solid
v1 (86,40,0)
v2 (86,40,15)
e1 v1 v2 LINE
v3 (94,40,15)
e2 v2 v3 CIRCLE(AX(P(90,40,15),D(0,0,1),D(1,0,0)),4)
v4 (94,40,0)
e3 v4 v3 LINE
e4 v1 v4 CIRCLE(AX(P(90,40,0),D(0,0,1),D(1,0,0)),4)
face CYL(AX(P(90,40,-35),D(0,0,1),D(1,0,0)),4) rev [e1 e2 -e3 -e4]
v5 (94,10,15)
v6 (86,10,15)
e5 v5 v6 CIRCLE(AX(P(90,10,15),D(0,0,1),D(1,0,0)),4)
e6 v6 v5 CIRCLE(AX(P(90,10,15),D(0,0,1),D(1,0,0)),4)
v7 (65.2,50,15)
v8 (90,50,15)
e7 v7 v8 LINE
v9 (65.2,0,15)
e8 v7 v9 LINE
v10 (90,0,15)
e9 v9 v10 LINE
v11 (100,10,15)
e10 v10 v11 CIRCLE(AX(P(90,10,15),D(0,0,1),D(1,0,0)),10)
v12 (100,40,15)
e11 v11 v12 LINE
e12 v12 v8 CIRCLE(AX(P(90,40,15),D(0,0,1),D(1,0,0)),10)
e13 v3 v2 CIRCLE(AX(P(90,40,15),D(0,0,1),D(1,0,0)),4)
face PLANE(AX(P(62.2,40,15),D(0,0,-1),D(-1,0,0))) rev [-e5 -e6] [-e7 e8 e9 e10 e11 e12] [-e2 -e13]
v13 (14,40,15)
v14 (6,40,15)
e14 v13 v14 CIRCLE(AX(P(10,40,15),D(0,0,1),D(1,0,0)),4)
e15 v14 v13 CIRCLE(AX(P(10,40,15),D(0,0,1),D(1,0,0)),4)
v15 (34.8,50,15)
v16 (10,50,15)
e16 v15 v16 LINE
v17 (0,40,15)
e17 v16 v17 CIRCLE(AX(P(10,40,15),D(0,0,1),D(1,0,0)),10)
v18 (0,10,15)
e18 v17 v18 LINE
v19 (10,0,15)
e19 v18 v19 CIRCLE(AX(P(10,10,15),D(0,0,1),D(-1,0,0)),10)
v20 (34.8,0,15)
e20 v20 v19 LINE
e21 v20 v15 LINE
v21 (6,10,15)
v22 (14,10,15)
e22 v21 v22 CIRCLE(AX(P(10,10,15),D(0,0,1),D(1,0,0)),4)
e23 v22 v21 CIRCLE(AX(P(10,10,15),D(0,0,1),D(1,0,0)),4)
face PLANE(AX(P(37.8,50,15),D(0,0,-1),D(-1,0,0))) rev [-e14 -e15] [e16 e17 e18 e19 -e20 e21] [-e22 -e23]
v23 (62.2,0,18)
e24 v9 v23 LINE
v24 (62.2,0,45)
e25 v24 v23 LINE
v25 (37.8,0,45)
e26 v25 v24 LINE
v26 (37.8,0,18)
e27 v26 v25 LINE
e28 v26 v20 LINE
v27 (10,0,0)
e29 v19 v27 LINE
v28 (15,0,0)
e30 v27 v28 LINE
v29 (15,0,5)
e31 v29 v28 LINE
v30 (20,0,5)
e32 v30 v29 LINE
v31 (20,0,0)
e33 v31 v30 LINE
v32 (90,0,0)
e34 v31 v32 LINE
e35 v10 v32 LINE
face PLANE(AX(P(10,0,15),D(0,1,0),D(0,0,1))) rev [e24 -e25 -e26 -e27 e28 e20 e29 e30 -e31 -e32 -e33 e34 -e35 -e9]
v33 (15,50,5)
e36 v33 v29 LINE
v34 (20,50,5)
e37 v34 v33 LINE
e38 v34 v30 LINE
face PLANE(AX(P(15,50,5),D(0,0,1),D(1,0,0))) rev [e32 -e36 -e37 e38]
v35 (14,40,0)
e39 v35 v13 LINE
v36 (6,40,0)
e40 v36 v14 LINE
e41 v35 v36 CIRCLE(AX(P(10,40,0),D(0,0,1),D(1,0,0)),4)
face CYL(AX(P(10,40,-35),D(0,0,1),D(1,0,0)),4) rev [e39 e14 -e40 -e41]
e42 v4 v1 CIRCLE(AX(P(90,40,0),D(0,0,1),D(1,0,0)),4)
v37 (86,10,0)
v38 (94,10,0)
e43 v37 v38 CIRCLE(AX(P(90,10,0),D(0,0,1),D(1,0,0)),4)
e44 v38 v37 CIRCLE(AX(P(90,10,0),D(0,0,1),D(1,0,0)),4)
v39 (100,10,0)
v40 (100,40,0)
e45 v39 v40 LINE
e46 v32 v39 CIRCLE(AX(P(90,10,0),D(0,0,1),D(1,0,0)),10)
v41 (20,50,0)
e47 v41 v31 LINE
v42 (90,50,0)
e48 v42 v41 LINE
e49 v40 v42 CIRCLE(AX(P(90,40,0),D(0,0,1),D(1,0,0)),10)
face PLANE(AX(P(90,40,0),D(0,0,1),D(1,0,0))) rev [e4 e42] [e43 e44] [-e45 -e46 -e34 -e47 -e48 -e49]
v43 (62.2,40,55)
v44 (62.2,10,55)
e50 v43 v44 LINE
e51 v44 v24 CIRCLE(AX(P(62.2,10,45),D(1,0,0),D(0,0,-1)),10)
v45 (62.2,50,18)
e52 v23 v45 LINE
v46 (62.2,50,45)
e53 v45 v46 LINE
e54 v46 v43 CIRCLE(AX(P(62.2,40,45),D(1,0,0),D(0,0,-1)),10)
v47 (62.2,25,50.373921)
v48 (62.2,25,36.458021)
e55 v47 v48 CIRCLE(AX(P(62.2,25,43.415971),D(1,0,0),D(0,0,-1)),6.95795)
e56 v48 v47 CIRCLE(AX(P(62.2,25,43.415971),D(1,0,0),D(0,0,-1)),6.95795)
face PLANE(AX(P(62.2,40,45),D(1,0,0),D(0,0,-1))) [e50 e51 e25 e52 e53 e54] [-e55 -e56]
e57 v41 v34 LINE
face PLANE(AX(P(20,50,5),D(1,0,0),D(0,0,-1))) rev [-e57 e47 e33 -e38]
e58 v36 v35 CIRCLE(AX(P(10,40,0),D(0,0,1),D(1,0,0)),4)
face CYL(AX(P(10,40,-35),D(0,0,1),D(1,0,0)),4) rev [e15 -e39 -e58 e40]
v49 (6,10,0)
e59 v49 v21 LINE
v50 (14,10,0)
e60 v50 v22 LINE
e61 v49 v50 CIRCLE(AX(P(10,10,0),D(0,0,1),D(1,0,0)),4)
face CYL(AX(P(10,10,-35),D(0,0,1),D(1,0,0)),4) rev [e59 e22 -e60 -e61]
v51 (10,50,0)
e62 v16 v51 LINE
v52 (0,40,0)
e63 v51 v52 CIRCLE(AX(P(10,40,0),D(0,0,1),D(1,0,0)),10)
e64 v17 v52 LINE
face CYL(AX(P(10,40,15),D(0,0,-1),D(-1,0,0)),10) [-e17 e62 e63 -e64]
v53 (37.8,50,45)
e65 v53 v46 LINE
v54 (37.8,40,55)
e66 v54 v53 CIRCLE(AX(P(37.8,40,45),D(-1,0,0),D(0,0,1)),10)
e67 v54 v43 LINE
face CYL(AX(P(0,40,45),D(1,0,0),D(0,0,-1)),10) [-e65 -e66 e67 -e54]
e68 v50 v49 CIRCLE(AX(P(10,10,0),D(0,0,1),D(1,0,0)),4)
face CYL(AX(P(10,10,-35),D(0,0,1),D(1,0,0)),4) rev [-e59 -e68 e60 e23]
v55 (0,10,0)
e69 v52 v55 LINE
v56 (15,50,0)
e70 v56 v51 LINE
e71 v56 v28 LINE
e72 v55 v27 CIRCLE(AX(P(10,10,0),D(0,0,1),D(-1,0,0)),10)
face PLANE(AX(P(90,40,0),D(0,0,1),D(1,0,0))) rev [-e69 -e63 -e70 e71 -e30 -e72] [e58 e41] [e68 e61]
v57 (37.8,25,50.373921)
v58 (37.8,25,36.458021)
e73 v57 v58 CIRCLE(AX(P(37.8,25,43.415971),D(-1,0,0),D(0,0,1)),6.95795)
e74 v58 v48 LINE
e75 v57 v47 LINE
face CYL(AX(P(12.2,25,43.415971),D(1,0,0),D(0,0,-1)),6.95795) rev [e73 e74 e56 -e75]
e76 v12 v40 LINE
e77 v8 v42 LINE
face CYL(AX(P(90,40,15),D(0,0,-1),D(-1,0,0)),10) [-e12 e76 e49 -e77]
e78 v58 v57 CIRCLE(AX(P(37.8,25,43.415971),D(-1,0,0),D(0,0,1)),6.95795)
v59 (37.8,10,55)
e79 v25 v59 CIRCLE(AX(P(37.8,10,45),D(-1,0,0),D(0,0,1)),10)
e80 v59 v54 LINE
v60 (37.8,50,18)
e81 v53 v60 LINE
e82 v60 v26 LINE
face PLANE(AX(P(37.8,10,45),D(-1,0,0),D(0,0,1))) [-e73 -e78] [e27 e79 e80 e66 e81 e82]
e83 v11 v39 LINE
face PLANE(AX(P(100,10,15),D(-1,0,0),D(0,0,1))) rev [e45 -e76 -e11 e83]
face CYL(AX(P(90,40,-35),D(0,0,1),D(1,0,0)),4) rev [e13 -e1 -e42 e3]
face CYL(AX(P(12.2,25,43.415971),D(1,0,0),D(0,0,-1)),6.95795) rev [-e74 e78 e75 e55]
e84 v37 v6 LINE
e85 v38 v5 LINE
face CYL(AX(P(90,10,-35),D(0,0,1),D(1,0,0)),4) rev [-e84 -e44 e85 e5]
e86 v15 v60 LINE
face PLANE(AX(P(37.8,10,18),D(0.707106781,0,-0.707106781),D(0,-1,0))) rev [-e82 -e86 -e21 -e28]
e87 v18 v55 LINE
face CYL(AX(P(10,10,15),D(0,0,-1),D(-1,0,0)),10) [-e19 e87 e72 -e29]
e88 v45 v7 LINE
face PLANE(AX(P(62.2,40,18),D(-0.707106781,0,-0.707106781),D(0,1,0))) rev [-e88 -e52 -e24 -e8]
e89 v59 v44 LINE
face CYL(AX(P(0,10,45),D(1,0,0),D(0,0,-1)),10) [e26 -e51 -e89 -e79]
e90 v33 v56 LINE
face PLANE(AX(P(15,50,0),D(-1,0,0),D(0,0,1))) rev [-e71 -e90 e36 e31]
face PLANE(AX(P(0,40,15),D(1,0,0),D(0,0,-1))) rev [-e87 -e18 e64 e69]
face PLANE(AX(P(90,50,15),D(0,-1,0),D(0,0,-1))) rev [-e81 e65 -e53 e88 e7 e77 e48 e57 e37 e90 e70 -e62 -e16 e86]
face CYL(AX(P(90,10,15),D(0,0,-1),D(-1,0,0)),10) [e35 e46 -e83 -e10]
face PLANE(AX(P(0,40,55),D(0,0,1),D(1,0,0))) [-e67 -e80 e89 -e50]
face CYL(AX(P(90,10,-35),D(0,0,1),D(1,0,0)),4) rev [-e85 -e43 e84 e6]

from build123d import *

# Parameters (mm, degrees)
BASE_PLATE_DEPTH              = 15
KNUCKLE_BLOCK_DEPTH           = 100
KNUCKLE_RELIEF_CUT_A_DEPTH    = 37.8
KNUCKLE_START                 = -37.8
KNUCKLE_RELIEF_CUT_B_DEPTH    = 37.8
PLATE_MOUNTING_HOLES_SKETCH_W = 5
PLATE_MOUNTING_HOLES_SKETCH_H = 5
PLATE_MOUNTING_HOLES_DEPTH    = 50
HINGE_PIN_HOLE_SKETCH_R       = 6.957950298
HINGE_PIN_HOLE_DEPTH          = 50
UPPER_MOUNTING_HOLES_SKETCH_R = 4
UPPER_MOUNTING_HOLES_DEPTH    = 50
KNUCKLE_CHAMFER_A_3X45_SIZE   = 3
KNUCKLE_CHAMFER_B_3X45_SIZE   = 3


with BuildPart() as part:
    # Base Plate Sketch → Base Plate (new body)
    with BuildSketch(Plane.XY):
        with BuildLine():
            Line((10, 0), (90, 0))
            ThreePointArc((90, 0), (97.071067812, 2.928932188), (100, 10))
            Line((100, 10), (100, 40))
            ThreePointArc((100, 40), (97.071067812, 47.071067812), (90, 50))
            Line((90, 50), (10, 50))
            ThreePointArc((10, 50), (2.928932188, 47.071067812), (0, 40))
            Line((0, 40), (0, 10))
            ThreePointArc((0, 10), (2.928932188, 2.928932188), (10, 0))
        make_face()
    extrude(amount=BASE_PLATE_DEPTH)

    # Knuckle Block Sketch → Knuckle Block (add)
    with BuildSketch(Plane(origin=(100, 0, 0), x_dir=(0, 0, -1), z_dir=(1, 0, 0))):
        with BuildLine():
            Line((-15, 50), (-45, 50))
            ThreePointArc((-45, 50), (-52.071067812, 47.071067812), (-55, 40))
            Line((-55, 40), (-55, 10))
            ThreePointArc((-55, 10), (-52.071067812, 2.928932188), (-45, 0))
            Line((-45, 0), (-15, 0))
            Line((-15, 0), (-15, 50))
        make_face()
    extrude(amount=-KNUCKLE_BLOCK_DEPTH)

    # Knuckle Relief Cut A Sketch → Knuckle Relief Cut A (cut)
    with BuildSketch(Plane(origin=(100, 0, 0), x_dir=(0, 0, -1), z_dir=(1, 0, 0))):
        with BuildLine():
            Line((-15, 40), (-15, 50))
            Line((-15, 50), (-45, 50))
            ThreePointArc((-45, 50), (-52.071067812, 47.071067812), (-55, 40))
            Line((-55, 40), (-55, 10))
            ThreePointArc((-55, 10), (-52.071067812, 2.928932188), (-45, 0))
            Line((-45, 0), (-15, 0))
            Line((-15, 0), (-15, 40))
        make_face()
    extrude(amount=-KNUCKLE_RELIEF_CUT_A_DEPTH, mode=Mode.SUBTRACT)

    # Knuckle Relief Cut B Sketch → Knuckle Relief Cut B (cut)
    with BuildSketch(Plane.ZY.offset(KNUCKLE_START)):
        with BuildLine():
            Line((15, 50), (45, 50))
            ThreePointArc((45, 50), (52.071067812, 47.071067812), (55, 40))
            Line((55, 40), (55, 10))
            ThreePointArc((55, 10), (52.071067812, 2.928932188), (45, 0))
            Line((45, 0), (15, 0))
            Line((15, 0), (15, 50))
        make_face()
    extrude(amount=KNUCKLE_RELIEF_CUT_B_DEPTH, mode=Mode.SUBTRACT)

    # Plate Mounting Holes Sketch → Plate Mounting Holes (cut)
    with BuildSketch(Plane.XZ):
        with Locations((17.5, 2.5)):
            Rectangle(PLATE_MOUNTING_HOLES_SKETCH_W, PLATE_MOUNTING_HOLES_SKETCH_H)
    extrude(amount=-PLATE_MOUNTING_HOLES_DEPTH, mode=Mode.SUBTRACT)

    # Hinge Pin Hole Sketch → Hinge Pin Hole (cut)
    with BuildSketch(Plane(origin=(62.2, 0, 0), x_dir=(0, 0, -1), z_dir=(1, 0, 0))):
        with Locations((-43.415970908, 25)):
            Circle(HINGE_PIN_HOLE_SKETCH_R)
    extrude(amount=-HINGE_PIN_HOLE_DEPTH, mode=Mode.SUBTRACT)

    # Upper Mounting Holes Sketch → Upper Mounting Holes (cut)
    with BuildSketch(Plane.XY.offset(15)):
        with Locations((90, 40)):
            Circle(UPPER_MOUNTING_HOLES_SKETCH_R)
        with Locations((90, 10)):
            Circle(UPPER_MOUNTING_HOLES_SKETCH_R)
        with Locations((10, 40)):
            Circle(UPPER_MOUNTING_HOLES_SKETCH_R)
        with Locations((10, 10)):
            Circle(UPPER_MOUNTING_HOLES_SKETCH_R)
    extrude(amount=-UPPER_MOUNTING_HOLES_DEPTH, mode=Mode.SUBTRACT)

    # Knuckle Chamfer A 3x45
    knuckle_chamfer_a_3x45_edges = [part.edges().sort_by_distance(p)[0] for p in [
        (62.2, 25, 15),
    ]]
    chamfer(knuckle_chamfer_a_3x45_edges, length=KNUCKLE_CHAMFER_A_3X45_SIZE)

    # Knuckle Chamfer B 3x45
    knuckle_chamfer_b_3x45_edges = [part.edges().sort_by_distance(p)[0] for p in [
        (37.8, 25, 15),
    ]]
    chamfer(knuckle_chamfer_b_3x45_edges, length=KNUCKLE_CHAMFER_B_3X45_SIZE)


solid = part.part
